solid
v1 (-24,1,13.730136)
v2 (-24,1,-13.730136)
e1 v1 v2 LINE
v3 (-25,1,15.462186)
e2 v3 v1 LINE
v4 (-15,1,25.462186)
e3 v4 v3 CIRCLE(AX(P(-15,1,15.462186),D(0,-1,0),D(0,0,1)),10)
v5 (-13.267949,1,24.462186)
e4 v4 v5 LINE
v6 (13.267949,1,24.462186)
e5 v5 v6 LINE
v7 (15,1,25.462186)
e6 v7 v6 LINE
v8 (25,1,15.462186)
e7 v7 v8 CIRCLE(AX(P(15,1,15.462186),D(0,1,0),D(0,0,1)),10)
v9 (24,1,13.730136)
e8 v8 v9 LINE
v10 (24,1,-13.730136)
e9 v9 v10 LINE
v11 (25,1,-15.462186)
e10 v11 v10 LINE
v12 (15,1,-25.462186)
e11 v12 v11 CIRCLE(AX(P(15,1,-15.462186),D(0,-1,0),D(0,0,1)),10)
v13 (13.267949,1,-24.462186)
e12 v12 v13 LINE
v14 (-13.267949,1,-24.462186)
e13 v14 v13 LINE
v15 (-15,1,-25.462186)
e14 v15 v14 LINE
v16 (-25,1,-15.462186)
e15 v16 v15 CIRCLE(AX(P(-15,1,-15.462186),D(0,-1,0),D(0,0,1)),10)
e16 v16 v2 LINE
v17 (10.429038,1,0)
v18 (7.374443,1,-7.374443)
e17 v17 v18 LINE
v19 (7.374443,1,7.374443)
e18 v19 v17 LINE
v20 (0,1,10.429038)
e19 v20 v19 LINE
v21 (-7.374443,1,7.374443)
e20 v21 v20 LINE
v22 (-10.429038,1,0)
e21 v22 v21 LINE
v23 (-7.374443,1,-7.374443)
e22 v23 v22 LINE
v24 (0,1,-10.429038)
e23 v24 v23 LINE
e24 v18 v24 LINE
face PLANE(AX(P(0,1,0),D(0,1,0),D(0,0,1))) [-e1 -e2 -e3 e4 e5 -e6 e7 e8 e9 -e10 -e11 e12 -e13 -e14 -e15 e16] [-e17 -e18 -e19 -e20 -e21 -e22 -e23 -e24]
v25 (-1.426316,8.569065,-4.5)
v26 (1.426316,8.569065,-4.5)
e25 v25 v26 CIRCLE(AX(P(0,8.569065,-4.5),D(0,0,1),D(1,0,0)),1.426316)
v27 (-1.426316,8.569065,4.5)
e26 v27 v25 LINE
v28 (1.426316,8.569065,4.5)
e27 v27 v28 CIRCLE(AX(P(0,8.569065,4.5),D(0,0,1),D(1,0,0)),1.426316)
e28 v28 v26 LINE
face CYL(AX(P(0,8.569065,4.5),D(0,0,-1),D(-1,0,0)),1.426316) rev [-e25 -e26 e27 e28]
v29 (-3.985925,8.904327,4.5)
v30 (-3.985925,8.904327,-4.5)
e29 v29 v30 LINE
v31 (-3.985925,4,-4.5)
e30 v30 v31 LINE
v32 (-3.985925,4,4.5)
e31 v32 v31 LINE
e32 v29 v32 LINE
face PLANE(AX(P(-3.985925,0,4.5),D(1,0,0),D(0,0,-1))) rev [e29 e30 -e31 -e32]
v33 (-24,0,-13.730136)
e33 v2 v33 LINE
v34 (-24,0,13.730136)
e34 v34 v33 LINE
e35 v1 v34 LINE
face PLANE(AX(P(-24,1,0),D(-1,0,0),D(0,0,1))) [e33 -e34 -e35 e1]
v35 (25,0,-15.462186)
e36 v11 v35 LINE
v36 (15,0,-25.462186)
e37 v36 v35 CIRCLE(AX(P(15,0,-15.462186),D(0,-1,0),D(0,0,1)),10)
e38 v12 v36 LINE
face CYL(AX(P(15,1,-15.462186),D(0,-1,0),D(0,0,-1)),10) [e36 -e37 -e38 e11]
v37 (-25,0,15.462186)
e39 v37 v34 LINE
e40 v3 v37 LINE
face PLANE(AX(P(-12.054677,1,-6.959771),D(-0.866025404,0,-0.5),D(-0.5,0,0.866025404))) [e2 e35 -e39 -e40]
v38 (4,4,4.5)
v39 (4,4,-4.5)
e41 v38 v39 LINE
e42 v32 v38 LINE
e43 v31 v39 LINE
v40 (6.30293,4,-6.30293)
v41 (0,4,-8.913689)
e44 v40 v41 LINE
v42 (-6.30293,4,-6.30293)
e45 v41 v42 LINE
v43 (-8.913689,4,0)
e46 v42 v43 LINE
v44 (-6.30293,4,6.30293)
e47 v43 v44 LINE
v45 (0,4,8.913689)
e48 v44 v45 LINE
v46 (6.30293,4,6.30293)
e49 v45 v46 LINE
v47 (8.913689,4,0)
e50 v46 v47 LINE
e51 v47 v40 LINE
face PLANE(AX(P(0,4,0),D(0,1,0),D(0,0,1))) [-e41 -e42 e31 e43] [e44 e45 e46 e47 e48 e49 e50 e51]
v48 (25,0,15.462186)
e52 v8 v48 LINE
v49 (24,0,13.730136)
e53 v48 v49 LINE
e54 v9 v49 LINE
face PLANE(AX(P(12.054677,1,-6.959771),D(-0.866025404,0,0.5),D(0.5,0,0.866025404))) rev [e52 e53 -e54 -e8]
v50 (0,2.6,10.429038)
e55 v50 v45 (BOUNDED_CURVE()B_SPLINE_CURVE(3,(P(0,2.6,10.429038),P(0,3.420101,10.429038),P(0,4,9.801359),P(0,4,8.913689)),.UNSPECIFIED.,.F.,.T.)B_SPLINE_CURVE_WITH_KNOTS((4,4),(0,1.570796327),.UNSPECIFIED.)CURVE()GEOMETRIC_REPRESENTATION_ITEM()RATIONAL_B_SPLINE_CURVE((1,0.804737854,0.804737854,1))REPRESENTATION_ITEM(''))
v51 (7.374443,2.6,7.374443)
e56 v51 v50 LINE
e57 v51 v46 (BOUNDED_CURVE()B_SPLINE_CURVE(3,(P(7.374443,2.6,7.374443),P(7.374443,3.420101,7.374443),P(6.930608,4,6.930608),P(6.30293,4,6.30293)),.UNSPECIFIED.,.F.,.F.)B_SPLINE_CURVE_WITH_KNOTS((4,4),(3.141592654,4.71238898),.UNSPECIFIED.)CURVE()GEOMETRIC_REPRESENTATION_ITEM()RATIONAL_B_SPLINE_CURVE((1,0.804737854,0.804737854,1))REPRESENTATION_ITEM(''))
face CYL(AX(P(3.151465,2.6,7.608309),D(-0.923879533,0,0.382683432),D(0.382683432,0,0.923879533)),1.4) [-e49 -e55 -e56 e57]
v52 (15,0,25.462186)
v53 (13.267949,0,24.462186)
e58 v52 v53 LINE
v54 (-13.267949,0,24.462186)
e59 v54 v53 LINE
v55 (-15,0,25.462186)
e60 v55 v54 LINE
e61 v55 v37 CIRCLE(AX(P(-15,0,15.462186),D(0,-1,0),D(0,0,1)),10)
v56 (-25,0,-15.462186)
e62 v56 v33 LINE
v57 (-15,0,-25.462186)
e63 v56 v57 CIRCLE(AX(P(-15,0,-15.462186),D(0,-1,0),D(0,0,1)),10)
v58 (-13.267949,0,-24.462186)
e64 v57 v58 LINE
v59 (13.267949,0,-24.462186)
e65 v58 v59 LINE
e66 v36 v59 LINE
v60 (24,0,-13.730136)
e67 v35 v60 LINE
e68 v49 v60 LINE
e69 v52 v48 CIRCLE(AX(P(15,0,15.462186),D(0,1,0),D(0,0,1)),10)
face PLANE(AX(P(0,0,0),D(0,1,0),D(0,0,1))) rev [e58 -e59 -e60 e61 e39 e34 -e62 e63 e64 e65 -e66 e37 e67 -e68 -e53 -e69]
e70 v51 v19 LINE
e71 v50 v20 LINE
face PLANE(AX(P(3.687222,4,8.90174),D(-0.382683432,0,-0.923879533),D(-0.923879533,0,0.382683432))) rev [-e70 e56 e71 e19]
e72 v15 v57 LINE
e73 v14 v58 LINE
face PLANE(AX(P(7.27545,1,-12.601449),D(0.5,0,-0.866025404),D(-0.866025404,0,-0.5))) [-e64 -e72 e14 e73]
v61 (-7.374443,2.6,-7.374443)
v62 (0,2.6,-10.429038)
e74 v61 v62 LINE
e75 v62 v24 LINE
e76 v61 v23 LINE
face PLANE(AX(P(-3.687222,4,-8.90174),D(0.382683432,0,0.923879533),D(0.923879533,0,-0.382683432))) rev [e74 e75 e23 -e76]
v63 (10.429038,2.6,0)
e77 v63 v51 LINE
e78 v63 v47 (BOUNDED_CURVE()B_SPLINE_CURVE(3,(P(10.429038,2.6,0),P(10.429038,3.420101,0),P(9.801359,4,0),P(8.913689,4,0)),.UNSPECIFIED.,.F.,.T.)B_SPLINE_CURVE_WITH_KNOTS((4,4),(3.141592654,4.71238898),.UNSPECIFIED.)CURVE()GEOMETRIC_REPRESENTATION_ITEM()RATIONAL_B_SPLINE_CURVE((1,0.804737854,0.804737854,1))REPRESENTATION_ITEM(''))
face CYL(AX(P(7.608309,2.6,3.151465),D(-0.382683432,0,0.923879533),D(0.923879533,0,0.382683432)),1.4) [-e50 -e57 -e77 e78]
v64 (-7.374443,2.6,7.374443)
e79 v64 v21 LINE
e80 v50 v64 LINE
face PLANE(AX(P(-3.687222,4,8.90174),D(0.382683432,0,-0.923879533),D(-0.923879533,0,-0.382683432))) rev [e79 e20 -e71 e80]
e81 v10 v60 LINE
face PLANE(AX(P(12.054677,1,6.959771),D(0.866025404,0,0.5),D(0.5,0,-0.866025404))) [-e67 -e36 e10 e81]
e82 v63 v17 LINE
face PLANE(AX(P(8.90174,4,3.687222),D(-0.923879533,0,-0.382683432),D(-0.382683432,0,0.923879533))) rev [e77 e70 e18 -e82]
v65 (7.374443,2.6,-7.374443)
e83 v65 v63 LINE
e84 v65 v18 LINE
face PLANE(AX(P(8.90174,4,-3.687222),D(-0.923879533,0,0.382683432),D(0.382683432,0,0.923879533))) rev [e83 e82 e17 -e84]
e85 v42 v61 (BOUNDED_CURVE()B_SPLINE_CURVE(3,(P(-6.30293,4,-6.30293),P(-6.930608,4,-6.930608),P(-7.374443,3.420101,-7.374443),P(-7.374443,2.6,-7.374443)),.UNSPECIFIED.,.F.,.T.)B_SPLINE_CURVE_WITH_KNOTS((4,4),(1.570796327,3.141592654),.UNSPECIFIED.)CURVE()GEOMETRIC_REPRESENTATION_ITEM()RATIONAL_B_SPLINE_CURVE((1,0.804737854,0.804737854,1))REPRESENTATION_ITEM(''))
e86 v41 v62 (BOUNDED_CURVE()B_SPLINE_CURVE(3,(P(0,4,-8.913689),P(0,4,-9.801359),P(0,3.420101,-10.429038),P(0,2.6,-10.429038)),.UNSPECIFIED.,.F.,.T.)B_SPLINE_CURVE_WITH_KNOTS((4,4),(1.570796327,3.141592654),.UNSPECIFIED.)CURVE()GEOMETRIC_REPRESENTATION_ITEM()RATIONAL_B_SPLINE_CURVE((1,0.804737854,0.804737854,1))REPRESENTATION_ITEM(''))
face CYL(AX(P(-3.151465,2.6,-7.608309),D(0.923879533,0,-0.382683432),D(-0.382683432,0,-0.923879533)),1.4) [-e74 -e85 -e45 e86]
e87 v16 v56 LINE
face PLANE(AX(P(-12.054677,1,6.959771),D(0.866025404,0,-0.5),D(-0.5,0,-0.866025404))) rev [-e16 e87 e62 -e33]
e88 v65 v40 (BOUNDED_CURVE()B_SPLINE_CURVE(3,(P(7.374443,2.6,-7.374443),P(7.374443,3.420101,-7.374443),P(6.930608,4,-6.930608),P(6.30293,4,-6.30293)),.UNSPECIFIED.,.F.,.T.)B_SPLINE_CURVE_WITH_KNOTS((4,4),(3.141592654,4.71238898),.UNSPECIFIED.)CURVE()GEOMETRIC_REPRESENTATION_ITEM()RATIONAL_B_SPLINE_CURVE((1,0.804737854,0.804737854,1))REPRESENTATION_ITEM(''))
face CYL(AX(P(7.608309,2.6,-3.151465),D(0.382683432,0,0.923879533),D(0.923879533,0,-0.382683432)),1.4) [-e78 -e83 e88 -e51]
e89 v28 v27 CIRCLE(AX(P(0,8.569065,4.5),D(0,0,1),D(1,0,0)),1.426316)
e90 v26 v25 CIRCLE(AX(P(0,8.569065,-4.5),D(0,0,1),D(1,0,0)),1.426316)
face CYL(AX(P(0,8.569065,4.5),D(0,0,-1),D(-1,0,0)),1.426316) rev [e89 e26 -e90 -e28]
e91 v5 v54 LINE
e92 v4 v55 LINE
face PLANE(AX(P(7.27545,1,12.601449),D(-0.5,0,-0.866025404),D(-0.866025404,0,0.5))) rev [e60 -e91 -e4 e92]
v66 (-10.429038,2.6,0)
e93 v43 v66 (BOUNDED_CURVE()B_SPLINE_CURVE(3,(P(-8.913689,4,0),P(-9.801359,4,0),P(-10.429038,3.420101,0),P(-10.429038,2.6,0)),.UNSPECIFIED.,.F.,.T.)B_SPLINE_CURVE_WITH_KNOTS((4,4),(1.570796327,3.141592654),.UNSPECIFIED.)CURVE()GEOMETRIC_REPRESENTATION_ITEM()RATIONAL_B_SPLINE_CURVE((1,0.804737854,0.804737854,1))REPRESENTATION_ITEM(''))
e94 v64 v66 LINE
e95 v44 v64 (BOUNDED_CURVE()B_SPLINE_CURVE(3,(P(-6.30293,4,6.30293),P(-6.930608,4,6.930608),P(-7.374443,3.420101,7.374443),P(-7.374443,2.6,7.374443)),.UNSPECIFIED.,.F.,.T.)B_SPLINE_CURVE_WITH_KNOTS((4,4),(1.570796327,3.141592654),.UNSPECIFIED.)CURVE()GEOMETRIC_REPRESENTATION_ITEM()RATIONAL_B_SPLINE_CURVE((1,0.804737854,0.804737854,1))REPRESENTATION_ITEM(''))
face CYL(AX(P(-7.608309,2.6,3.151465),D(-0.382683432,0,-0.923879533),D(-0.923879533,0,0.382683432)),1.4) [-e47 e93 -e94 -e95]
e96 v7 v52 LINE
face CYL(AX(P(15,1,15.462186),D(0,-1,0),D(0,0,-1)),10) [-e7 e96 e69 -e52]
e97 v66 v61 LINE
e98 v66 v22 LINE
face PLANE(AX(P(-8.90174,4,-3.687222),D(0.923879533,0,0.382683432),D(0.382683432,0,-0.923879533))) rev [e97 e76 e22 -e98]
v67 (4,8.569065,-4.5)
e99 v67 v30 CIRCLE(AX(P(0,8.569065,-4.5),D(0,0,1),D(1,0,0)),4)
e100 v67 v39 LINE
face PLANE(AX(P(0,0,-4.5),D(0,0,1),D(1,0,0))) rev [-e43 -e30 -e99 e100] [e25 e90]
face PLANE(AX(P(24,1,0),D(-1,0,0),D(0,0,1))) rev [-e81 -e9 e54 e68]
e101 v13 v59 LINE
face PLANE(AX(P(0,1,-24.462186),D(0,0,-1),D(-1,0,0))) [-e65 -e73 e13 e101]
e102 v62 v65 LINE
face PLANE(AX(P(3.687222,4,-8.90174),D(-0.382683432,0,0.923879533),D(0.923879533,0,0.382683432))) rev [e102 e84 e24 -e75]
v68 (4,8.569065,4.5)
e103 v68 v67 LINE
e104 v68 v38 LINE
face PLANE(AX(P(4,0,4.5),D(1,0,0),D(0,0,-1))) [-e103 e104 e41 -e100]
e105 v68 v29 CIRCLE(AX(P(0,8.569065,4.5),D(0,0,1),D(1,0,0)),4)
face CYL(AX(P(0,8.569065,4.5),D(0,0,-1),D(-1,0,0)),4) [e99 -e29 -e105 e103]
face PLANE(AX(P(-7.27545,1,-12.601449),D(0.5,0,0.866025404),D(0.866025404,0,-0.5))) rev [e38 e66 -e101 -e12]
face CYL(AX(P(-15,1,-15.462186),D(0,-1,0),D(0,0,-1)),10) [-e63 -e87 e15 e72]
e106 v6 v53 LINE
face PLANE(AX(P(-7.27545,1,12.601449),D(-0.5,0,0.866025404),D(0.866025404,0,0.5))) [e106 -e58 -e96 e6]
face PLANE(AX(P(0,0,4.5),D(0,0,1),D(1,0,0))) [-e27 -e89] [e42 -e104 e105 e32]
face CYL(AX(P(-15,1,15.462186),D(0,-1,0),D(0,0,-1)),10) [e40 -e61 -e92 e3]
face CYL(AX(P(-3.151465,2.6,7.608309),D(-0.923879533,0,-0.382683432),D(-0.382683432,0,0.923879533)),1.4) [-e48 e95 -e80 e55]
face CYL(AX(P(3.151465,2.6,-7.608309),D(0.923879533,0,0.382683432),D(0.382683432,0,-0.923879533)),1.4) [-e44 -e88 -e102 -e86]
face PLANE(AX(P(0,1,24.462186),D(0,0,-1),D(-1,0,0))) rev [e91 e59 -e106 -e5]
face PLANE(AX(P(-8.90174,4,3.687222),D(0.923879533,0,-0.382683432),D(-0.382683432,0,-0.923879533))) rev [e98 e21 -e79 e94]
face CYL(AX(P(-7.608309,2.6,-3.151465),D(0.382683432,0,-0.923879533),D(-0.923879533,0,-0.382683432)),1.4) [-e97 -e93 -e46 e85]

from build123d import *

# Parameters (mm, degrees)
BOSS_EXTRUDE1_DEPTH = 1
BOSS_EXTRUDE2_DEPTH = 3
FILLET1_R           = 1.4
SKETCH3_R           = 1.426316434
BOSS_EXTRUDE3_DEPTH = 4.5


with BuildPart() as part:
    # Sketch1 → Boss-Extrude1 (new body)
    with BuildSketch(Plane(origin=(0, 0, 0), x_dir=(1, 0, 0), z_dir=(0, 1, 0))):
        with BuildLine():
            Line((-15, -25.462186482), (-13.267949192, -24.462186482))
            Line((-13.267949192, -24.462186482), (13.267949192, -24.462186482))
            Line((13.267949192, -24.462186482), (15, -25.462186482))
            ThreePointArc((15, -25.462186482), (22.071067812, -22.533254294), (25, -15.462186482))
            Line((25, -15.462186482), (24, -13.730135674))
            Line((24, -13.730135674), (24, 13.730135674))
            Line((24, 13.730135674), (25, 15.462186482))
            ThreePointArc((25, 15.462186482), (22.071067812, 22.533254294), (15, 25.462186482))
            Line((15, 25.462186482), (13.267949192, 24.462186482))
            Line((13.267949192, 24.462186482), (-13.267949192, 24.462186482))
            Line((-13.267949192, 24.462186482), (-15, 25.462186482))
            ThreePointArc((-15, 25.462186482), (-22.071067812, 22.533254294), (-25, 15.462186482))
            Line((-25, 15.462186482), (-24, 13.730135674))
            Line((-24, 13.730135674), (-24, -13.730135674))
            Line((-24, -13.730135674), (-25, -15.462186482))
            ThreePointArc((-25, -15.462186482), (-22.071067812, -22.533254294), (-15, -25.462186482))
        make_face()
    extrude(amount=BOSS_EXTRUDE1_DEPTH)

    # Sketch2 → Boss-Extrude2 (add)
    with BuildSketch(Plane(origin=(0, 1, 0), x_dir=(1, 0, 0), z_dir=(0, 1, 0))):
        Polygon((0, -10.429037626), (7.374443227, -7.374443227), (10.429037626, 0), (-10.429037626, 0), (-7.374443227, -7.374443227), align=None)
        Polygon((0, 10.429037626), (-7.374443227, 7.374443227), (-10.429037626, 0), (10.429037626, 0), (7.374443227, 7.374443227), align=None)
    extrude(amount=BOSS_EXTRUDE2_DEPTH)

    # Fillet1
    fillet1_edges = [part.edges().sort_by_distance(p)[0] for p in [
        (3.687221613, 4, 8.901740426),
        (8.901740426, 4, 3.687221613),
        (8.901740426, 4, -3.687221613),
        (3.687221613, 4, -8.901740426),
        (-3.687221613, 4, -8.901740426),
        (-8.901740426, 4, -3.687221613),
        (-8.901740426, 4, 3.687221613),
        (-3.687221613, 4, 8.901740426),
    ]]
    fillet(fillet1_edges, radius=FILLET1_R)

    # Sketch3 → Boss-Extrude3 (add, symmetric)
    with BuildSketch(Plane.XY):
        with BuildLine():
            ThreePointArc((4, 8.569064594), (0.167778924, 12.565544324), (-3.985925116, 8.904327129))
            Line((-3.985925116, 8.904327129), (-3.985925116, 4))
            Line((-3.985925116, 4), (4, 4))
            Line((4, 4), (4, 8.569064594))
        make_face()
        with Locations((0, 8.569064594)):
            Circle(SKETCH3_R, mode=Mode.SUBTRACT)
    extrude(amount=BOSS_EXTRUDE3_DEPTH, both=True)


solid = part.part
